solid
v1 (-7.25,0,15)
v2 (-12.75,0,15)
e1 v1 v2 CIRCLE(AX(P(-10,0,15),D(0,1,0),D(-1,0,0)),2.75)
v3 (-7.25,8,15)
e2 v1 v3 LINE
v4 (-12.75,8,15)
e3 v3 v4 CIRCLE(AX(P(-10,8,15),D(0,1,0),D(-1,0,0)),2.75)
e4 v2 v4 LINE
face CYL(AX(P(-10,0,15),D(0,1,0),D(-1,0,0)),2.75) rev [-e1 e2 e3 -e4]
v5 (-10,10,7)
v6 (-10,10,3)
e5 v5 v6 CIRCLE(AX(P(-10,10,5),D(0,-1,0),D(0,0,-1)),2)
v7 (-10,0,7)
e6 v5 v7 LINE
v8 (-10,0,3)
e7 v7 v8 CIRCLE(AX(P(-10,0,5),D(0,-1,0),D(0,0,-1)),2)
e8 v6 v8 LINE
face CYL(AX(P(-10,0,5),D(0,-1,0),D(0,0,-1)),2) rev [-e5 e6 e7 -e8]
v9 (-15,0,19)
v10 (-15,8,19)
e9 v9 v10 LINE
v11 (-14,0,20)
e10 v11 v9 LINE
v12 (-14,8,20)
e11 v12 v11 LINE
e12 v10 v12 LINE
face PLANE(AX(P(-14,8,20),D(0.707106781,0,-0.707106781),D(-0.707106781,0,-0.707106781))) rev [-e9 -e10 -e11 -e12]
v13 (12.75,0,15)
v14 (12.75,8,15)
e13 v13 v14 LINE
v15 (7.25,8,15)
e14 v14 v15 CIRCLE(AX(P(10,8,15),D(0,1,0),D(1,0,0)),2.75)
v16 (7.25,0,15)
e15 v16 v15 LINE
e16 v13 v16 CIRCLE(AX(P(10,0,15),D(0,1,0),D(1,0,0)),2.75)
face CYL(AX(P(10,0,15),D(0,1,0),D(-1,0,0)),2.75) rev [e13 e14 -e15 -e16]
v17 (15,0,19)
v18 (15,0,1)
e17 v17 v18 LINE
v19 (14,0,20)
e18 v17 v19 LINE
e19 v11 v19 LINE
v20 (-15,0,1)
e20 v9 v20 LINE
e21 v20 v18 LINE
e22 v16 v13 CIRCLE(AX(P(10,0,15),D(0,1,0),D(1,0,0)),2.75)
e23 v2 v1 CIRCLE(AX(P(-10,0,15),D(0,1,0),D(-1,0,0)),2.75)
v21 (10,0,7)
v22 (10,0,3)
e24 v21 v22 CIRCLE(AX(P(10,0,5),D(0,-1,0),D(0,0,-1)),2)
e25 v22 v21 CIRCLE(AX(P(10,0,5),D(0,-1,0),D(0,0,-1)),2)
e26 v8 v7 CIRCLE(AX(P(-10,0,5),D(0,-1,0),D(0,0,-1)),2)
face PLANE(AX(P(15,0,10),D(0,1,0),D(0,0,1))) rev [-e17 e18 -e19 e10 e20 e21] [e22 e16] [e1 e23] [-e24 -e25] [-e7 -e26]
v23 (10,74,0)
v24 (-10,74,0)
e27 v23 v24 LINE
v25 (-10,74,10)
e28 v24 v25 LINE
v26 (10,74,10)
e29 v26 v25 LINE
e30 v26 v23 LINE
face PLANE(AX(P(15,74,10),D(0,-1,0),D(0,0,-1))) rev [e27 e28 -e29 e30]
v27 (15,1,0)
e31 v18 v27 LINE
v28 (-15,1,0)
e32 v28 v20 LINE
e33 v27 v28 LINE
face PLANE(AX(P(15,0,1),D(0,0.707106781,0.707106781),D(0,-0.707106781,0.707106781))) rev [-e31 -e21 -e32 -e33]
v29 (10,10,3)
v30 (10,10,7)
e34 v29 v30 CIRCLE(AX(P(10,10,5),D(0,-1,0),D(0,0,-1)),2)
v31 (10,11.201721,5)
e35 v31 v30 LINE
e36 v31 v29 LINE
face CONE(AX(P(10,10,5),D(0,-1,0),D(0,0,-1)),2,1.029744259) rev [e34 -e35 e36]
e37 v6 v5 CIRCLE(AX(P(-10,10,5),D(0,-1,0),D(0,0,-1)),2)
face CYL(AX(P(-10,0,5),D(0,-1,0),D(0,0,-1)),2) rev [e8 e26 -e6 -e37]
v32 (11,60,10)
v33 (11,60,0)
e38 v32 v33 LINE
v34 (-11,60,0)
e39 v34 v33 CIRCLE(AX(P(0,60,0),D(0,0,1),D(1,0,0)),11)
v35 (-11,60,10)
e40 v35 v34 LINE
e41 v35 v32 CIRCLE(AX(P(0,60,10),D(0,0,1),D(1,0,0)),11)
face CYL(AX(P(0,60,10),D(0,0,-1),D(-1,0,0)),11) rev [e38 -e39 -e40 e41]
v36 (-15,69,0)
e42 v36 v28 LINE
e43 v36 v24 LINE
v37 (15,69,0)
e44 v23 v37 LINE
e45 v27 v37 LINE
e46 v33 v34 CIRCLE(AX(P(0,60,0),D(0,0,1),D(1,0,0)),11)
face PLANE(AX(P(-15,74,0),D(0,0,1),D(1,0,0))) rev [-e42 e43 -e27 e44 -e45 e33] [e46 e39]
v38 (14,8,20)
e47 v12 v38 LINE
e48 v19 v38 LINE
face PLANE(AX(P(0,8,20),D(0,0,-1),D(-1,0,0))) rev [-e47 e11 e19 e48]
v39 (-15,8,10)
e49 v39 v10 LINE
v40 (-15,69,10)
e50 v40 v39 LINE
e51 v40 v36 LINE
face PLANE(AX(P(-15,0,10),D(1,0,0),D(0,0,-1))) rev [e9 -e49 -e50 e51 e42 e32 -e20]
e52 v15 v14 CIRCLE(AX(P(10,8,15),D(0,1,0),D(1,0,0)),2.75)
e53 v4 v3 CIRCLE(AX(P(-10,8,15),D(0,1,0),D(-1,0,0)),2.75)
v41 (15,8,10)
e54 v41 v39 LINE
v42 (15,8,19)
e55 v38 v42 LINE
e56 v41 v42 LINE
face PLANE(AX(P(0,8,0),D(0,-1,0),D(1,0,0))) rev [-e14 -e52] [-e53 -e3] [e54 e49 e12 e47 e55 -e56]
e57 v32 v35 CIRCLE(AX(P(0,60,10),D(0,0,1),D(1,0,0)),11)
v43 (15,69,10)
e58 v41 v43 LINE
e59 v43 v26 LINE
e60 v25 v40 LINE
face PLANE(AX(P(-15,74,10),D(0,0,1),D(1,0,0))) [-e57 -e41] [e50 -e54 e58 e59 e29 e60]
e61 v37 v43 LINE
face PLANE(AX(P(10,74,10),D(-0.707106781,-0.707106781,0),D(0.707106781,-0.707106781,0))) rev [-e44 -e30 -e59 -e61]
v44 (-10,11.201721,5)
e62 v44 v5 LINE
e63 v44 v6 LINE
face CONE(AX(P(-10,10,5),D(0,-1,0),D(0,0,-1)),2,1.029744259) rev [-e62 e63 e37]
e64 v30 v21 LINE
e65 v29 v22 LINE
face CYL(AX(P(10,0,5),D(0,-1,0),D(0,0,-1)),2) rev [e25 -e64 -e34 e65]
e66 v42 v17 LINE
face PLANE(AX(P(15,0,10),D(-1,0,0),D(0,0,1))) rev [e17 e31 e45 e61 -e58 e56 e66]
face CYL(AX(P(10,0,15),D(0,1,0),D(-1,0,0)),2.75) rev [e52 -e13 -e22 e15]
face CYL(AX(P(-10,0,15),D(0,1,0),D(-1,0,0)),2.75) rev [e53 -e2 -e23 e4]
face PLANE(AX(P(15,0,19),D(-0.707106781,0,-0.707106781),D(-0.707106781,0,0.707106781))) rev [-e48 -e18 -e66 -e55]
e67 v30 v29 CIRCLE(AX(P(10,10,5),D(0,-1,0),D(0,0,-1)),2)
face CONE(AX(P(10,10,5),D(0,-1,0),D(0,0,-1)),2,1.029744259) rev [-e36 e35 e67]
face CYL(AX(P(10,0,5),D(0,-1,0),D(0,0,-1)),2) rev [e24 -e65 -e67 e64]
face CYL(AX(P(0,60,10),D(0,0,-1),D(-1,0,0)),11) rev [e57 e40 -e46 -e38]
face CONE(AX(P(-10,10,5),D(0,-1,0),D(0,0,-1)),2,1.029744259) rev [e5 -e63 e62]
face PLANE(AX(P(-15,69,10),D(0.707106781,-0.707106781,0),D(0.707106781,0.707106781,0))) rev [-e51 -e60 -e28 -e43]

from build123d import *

# Parameters (mm, degrees)
SKETCH1_W                    = 30
SKETCH1_H                    = 74
SKETCH1_R                    = 11
BOSS_EXTRUDE1_DEPTH          = 10
SKETCH3_W                    = 15
SKETCH3_H                    = 10
BOSS_EXTRUDE2_DEPTH          = 8
SKETCH4_R                    = 2.75
CUT_EXTRUDE1_DEPTH           = 71.576199954
F_4_0_4_DIAMETER_HOLE1_D     = 4
F_4_0_4_DIAMETER_HOLE1_DEPTH = 10
F_4_0_4_DIAMETER_HOLE1_TIP   = 1.201721238
CHAMFER1_SIZE                = 5
CHAMFER2_SIZE                = 1


with BuildPart() as part:
    # Sketch1 → Boss-Extrude1 (new body)
    with BuildSketch(Plane.XY):
        with Locations((0, 37)):
            Rectangle(SKETCH1_W, SKETCH1_H)
        with Locations((0, 60)):
            Circle(SKETCH1_R, mode=Mode.SUBTRACT)
    extrude(amount=BOSS_EXTRUDE1_DEPTH)

    # Sketch3 → Boss-Extrude2 (add)
    with BuildSketch(Plane.XZ):
        with Locations((-7.5, 15)):
            Rectangle(SKETCH3_W, SKETCH3_H)
        with Locations((7.5, 15)):
            Rectangle(SKETCH3_W, SKETCH3_H)
    extrude(amount=-BOSS_EXTRUDE2_DEPTH)

    # Sketch4 → Cut-Extrude1 (cut, through all)
    with BuildSketch(Plane(origin=(0, 8, 0), x_dir=(-1, 0, 0), z_dir=(0, 1, 0))):
        with Locations((10, 15)):
            Circle(SKETCH4_R)
        with Locations(Location((-10, 15, 0), (0, 0, 180))):
            Circle(SKETCH4_R)
    extrude(amount=-CUT_EXTRUDE1_DEPTH, mode=Mode.SUBTRACT)

    # Ø4.0 (4) Diameter Hole1
    with Locations(Plane.XZ):
        with Locations((-10, 5), (10, 5)):
            Hole(F_4_0_4_DIAMETER_HOLE1_D / 2, depth=F_4_0_4_DIAMETER_HOLE1_DEPTH)
            with Locations((0, 0, -(F_4_0_4_DIAMETER_HOLE1_DEPTH + F_4_0_4_DIAMETER_HOLE1_TIP / 2))):  # 118° drill point
                Cone(0, F_4_0_4_DIAMETER_HOLE1_D / 2, F_4_0_4_DIAMETER_HOLE1_TIP, mode=Mode.SUBTRACT)

    # Chamfer1
    chamfer1_edges = [part.edges().sort_by_distance(p)[0] for p in [
        (-15, 74, 5),
        (15, 74, 5),
    ]]
    chamfer(chamfer1_edges, length=CHAMFER1_SIZE)

    # Chamfer2
    chamfer2_edges = [part.edges().sort_by_distance(p)[0] for p in [
        (-15, 4, 20),
        (15, 4, 20),
        (0, 0, 0),
    ]]
    chamfer(chamfer2_edges, length=CHAMFER2_SIZE)


solid = part.part
